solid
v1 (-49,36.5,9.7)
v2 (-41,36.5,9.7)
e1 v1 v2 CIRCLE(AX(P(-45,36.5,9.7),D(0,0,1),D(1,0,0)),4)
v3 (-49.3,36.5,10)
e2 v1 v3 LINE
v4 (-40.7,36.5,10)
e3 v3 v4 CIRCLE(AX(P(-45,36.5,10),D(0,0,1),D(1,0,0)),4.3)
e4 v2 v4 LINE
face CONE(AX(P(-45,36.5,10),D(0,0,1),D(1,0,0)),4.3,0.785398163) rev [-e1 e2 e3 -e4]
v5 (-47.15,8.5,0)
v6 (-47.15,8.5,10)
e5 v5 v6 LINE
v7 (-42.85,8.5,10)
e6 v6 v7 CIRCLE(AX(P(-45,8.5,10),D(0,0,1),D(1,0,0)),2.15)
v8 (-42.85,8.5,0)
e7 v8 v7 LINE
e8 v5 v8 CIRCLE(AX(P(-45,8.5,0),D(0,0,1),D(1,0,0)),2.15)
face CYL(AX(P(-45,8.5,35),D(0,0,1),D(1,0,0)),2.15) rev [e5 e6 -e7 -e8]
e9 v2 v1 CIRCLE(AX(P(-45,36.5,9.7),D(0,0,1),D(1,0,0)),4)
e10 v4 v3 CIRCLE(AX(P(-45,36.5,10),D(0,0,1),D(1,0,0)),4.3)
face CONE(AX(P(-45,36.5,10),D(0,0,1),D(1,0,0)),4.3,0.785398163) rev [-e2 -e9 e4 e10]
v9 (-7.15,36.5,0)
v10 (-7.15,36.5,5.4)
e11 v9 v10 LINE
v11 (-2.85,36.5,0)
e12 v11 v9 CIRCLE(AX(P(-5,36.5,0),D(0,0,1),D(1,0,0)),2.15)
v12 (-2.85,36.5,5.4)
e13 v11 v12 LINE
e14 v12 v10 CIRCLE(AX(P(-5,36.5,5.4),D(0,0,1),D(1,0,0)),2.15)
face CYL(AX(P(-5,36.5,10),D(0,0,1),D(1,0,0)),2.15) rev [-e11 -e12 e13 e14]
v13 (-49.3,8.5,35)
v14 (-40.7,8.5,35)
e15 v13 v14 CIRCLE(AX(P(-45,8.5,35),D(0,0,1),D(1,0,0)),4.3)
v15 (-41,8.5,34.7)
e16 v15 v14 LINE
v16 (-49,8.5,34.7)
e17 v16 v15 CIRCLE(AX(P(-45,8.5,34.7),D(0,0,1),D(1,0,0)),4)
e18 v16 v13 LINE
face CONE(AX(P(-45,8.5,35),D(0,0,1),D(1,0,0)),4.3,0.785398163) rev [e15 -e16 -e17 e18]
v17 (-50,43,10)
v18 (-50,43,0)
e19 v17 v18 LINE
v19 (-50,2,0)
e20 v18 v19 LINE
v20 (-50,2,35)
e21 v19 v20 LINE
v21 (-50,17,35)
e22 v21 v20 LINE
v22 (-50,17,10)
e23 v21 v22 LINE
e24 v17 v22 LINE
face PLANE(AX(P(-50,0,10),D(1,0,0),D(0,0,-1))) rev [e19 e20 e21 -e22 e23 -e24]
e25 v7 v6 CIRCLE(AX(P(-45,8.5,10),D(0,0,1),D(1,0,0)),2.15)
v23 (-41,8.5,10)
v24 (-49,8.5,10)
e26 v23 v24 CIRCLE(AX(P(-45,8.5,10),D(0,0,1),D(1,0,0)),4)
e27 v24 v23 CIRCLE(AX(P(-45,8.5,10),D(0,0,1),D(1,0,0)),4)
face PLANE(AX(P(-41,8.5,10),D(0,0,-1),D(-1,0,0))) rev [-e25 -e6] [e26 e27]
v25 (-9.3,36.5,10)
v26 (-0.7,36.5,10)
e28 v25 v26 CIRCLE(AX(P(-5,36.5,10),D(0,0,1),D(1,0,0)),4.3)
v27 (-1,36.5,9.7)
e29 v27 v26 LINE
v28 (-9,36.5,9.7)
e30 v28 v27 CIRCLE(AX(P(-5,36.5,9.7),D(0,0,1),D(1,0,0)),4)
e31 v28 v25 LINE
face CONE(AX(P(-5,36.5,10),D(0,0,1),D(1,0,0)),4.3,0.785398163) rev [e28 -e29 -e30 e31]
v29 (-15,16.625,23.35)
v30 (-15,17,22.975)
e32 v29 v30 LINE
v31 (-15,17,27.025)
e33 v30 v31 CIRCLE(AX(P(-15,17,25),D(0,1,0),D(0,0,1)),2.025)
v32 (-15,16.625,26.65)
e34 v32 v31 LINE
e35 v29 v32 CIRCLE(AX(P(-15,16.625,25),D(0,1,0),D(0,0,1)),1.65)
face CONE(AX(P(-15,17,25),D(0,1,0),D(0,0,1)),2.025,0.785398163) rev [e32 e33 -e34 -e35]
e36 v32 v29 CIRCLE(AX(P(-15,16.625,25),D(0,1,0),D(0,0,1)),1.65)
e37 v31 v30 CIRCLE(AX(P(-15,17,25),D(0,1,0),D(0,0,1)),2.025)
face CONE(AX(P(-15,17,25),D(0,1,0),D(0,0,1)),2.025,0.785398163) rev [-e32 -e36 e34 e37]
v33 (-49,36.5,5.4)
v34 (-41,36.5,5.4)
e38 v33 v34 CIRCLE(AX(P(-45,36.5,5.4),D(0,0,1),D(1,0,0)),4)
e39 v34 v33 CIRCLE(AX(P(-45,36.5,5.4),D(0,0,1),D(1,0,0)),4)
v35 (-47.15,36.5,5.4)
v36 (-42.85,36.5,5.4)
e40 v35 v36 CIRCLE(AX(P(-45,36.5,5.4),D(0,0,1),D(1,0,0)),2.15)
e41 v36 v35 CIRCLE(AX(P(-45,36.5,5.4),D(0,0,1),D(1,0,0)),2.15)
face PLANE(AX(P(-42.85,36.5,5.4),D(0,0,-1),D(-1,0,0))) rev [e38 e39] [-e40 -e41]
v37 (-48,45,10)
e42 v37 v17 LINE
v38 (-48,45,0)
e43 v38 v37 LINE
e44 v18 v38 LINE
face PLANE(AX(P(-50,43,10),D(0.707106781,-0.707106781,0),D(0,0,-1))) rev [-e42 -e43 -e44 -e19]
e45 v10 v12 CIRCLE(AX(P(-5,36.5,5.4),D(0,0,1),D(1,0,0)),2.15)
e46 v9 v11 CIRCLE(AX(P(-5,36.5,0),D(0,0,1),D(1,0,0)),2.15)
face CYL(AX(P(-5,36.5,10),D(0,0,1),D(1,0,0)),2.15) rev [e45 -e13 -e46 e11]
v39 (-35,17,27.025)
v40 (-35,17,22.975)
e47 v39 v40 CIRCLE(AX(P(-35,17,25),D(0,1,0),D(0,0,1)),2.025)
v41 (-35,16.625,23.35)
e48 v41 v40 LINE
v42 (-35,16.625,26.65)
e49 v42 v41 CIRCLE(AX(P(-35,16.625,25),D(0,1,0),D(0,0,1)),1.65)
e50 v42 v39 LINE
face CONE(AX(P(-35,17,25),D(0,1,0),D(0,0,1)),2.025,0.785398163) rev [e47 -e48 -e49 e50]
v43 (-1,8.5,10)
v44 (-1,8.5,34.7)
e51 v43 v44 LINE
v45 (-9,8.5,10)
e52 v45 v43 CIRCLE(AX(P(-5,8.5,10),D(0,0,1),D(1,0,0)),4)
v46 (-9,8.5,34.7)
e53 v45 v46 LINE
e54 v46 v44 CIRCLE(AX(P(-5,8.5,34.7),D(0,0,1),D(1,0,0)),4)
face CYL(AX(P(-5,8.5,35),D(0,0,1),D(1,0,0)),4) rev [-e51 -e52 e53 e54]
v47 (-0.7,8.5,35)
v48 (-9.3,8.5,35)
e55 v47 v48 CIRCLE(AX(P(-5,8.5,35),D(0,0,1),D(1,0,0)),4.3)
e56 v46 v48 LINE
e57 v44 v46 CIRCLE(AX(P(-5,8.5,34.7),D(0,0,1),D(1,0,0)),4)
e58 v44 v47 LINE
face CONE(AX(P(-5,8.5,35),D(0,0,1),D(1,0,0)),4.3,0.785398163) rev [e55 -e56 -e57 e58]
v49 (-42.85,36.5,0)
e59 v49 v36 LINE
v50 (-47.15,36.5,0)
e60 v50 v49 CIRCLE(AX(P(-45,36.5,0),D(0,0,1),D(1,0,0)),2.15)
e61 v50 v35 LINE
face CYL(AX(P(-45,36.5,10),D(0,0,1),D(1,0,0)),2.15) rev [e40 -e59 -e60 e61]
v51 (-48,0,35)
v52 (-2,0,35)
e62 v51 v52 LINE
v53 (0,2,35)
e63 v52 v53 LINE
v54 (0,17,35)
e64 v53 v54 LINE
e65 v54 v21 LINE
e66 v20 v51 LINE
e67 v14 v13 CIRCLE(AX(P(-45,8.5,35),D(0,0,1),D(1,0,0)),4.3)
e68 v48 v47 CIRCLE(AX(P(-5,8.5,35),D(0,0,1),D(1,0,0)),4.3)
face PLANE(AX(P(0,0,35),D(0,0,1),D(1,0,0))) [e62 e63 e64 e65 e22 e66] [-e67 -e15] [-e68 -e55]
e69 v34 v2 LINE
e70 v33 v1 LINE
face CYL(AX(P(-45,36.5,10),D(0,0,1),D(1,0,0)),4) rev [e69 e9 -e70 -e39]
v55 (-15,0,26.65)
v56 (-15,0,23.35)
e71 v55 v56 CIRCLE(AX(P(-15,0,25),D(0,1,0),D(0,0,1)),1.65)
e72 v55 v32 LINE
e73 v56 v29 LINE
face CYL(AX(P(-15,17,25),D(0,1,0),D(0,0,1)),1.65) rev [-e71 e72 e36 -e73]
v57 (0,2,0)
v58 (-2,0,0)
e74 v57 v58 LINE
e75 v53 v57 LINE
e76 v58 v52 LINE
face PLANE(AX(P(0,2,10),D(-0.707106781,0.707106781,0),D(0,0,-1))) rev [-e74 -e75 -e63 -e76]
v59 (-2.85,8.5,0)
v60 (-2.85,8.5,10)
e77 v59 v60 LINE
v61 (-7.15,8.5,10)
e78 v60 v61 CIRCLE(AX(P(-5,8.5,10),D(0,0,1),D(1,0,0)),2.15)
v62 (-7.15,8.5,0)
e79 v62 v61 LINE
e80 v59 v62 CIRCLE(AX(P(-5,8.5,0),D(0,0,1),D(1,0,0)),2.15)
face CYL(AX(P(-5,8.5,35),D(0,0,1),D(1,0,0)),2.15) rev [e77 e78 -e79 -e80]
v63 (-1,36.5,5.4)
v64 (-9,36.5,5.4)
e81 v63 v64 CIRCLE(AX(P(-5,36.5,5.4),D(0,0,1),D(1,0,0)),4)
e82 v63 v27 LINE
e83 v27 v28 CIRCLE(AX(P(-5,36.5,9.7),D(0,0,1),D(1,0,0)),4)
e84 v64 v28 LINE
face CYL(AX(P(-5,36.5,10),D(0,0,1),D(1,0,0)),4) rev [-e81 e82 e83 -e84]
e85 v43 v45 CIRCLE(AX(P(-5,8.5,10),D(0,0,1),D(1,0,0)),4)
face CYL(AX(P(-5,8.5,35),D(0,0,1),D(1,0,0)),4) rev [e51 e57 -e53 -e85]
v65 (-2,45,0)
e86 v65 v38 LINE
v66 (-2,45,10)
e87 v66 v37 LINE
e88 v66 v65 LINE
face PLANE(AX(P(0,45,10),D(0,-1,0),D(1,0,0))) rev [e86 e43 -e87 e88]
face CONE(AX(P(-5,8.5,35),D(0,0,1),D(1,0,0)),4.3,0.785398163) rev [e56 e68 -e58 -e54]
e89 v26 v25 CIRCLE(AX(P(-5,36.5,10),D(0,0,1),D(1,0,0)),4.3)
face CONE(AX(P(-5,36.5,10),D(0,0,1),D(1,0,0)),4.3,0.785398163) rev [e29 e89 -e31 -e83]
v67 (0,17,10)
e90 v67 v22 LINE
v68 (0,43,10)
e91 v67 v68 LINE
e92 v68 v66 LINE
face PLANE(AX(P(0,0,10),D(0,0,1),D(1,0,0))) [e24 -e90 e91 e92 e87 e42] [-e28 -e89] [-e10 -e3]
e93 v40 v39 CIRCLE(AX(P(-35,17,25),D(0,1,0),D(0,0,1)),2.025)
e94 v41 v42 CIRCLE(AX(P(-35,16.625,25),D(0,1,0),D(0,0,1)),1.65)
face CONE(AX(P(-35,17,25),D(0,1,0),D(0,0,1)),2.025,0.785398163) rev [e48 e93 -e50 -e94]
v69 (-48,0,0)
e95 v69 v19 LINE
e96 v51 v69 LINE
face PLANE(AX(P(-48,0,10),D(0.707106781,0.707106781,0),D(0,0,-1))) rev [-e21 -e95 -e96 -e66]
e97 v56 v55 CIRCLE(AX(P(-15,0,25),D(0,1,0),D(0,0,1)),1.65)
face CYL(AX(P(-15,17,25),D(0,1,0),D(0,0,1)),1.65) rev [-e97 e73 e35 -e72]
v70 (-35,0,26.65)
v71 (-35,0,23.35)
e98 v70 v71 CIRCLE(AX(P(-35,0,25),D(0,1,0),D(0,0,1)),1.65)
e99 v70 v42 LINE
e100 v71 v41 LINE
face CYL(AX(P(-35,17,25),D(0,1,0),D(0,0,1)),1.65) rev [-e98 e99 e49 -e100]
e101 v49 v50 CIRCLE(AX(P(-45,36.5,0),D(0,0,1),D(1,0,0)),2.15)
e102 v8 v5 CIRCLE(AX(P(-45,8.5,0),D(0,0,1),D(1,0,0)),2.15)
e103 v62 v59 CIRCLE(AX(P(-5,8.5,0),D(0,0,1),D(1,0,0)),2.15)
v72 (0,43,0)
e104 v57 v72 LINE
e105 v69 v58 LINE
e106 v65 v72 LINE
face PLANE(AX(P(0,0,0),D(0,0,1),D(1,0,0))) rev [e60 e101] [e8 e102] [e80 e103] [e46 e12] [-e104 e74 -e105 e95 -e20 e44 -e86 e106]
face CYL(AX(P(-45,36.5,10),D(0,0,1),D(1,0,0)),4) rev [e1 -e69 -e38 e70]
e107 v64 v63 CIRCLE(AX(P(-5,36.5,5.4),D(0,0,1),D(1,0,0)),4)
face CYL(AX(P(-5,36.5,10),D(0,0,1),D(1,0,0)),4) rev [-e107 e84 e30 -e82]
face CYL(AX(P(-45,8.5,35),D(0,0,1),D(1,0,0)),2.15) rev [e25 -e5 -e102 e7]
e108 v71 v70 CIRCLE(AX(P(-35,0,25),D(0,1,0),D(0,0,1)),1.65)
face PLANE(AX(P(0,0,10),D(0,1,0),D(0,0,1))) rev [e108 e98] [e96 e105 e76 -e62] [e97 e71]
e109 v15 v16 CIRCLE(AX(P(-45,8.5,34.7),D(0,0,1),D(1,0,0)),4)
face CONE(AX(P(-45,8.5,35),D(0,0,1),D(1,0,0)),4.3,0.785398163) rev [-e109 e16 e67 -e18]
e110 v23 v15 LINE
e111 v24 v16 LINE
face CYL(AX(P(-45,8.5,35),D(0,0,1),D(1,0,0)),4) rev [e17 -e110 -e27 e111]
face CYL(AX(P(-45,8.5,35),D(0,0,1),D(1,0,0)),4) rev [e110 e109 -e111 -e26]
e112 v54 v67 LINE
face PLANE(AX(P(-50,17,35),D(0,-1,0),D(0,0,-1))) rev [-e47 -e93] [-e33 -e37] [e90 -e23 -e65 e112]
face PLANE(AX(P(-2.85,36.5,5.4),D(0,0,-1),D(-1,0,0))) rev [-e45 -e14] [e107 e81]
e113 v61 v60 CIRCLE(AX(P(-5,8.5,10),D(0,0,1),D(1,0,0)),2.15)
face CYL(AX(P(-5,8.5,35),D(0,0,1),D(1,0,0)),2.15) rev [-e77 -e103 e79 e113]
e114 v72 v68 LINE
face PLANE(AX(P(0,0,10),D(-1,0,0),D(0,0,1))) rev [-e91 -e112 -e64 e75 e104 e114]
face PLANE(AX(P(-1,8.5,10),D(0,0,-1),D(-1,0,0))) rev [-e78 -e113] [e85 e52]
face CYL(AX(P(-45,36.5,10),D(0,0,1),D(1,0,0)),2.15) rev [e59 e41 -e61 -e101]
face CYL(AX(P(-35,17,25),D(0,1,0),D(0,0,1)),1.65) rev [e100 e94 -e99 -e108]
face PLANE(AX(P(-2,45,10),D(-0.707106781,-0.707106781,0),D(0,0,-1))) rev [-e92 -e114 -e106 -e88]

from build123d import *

# Parameters (mm, degrees)
SKETCH_1_W                   = 50
SKETCH_1_H                   = 45
EXTRUDE_1_DEPTH              = 10
SKETCH_6_W                   = 50
SKETCH_6_H                   = 17
EXTRUDE_2_DEPTH              = 25
CHAMFER_1_SIZE               = 2
HOLE_WIZARD_1_AT_2_COUNT     = 2
HOLE_WIZARD_1_AT_2_PITCH     = 40
HOLE_WIZARD_2_AT_2_COUNT     = 2
HOLE_WIZARD_2_AT_2_PITCH     = 40
HOLE_WIZARD_M4_1_D           = 3.3
HOLE_WIZARD_M4_1_CSINK_D     = 4.05
HOLE_WIZARD_M4_1_CSINK_ANGLE = 90


with BuildPart() as part:
    # 草图1 → 凸台-拉伸1 (new body)
    with BuildSketch(Plane.XY):
        with Locations((-25, 22.5)):
            Rectangle(SKETCH_1_W, SKETCH_1_H)
    extrude(amount=EXTRUDE_1_DEPTH)

    # 草图6 → 凸台-拉伸2 (add)
    with BuildSketch(Plane.XY.offset(10)):
        with Locations((-25, 8.5)):
            Rectangle(SKETCH_6_W, SKETCH_6_H)
    extrude(amount=EXTRUDE_2_DEPTH)

    # 倒角1
    chamfer_1_edges = [part.edges().sort_by_distance(p)[0] for p in [
        (0, 0, 17.5),
        (-50, 0, 17.5),
        (-50, 45, 5),
        (0, 45, 5),
    ]]
    chamfer(chamfer_1_edges, length=CHAMFER_1_SIZE)

    # 草图4 → 打孔尺寸(%根据)内六角圆柱头螺钉的类型1 (revolve, cut)
    with BuildSketch(Plane(origin=(-45, 36.5, 10), x_dir=(0, -1, 0), z_dir=(1, 0, 0))):
        Polygon((0, 0), (0, 11.291850331), (2.15, 10), (2.15, 4.6), (4, 4.6), (4, 0.3), (4.3, 0), align=None)
    hole_wizard_1 = revolve(axis=Axis((-45, 36.5, 16.35), (0, 0, -1)), mode=Mode.SUBTRACT)

    # 打孔尺寸(%根据)内六角圆柱头螺钉的类型1 at 2: 打孔尺寸(%根据)内六角圆柱头螺钉的类型1 ×2
    with Locations(*[(i * HOLE_WIZARD_1_AT_2_PITCH, 0, 0) for i in range(1, HOLE_WIZARD_1_AT_2_COUNT)]):
        add(hole_wizard_1, mode=Mode.SUBTRACT)

    # 草图8 → 打孔尺寸(%根据)内六角圆柱头螺钉的类型2 (revolve, cut)
    with BuildSketch(Plane(origin=(-45, 8.5, 35), x_dir=(0, -1, 0), z_dir=(1, 0, 0))):
        Polygon((0, 0), (0, 35), (2.15, 35), (2.15, 25), (4, 25), (4, 0.3), (4.3, 0), align=None)
    hole_wizard_2 = revolve(axis=Axis((-45, 8.5, 41.35), (0, 0, -1)), mode=Mode.SUBTRACT)

    # 打孔尺寸(%根据)内六角圆柱头螺钉的类型2 at 2: 打孔尺寸(%根据)内六角圆柱头螺钉的类型2 ×2
    with Locations(*[(i * HOLE_WIZARD_2_AT_2_PITCH, 0, 0) for i in range(1, HOLE_WIZARD_2_AT_2_COUNT)]):
        add(hole_wizard_2, mode=Mode.SUBTRACT)

    # M4 螺纹孔1 (through all)
    with Locations(Plane(origin=(0, 17, 0), x_dir=(1, 0, 0), z_dir=(0, 1, 0))):
        with Locations((-35, -25), (-15, -25)):
            CounterSinkHole(HOLE_WIZARD_M4_1_D / 2, HOLE_WIZARD_M4_1_CSINK_D / 2, counter_sink_angle=HOLE_WIZARD_M4_1_CSINK_ANGLE)


solid = part.part
